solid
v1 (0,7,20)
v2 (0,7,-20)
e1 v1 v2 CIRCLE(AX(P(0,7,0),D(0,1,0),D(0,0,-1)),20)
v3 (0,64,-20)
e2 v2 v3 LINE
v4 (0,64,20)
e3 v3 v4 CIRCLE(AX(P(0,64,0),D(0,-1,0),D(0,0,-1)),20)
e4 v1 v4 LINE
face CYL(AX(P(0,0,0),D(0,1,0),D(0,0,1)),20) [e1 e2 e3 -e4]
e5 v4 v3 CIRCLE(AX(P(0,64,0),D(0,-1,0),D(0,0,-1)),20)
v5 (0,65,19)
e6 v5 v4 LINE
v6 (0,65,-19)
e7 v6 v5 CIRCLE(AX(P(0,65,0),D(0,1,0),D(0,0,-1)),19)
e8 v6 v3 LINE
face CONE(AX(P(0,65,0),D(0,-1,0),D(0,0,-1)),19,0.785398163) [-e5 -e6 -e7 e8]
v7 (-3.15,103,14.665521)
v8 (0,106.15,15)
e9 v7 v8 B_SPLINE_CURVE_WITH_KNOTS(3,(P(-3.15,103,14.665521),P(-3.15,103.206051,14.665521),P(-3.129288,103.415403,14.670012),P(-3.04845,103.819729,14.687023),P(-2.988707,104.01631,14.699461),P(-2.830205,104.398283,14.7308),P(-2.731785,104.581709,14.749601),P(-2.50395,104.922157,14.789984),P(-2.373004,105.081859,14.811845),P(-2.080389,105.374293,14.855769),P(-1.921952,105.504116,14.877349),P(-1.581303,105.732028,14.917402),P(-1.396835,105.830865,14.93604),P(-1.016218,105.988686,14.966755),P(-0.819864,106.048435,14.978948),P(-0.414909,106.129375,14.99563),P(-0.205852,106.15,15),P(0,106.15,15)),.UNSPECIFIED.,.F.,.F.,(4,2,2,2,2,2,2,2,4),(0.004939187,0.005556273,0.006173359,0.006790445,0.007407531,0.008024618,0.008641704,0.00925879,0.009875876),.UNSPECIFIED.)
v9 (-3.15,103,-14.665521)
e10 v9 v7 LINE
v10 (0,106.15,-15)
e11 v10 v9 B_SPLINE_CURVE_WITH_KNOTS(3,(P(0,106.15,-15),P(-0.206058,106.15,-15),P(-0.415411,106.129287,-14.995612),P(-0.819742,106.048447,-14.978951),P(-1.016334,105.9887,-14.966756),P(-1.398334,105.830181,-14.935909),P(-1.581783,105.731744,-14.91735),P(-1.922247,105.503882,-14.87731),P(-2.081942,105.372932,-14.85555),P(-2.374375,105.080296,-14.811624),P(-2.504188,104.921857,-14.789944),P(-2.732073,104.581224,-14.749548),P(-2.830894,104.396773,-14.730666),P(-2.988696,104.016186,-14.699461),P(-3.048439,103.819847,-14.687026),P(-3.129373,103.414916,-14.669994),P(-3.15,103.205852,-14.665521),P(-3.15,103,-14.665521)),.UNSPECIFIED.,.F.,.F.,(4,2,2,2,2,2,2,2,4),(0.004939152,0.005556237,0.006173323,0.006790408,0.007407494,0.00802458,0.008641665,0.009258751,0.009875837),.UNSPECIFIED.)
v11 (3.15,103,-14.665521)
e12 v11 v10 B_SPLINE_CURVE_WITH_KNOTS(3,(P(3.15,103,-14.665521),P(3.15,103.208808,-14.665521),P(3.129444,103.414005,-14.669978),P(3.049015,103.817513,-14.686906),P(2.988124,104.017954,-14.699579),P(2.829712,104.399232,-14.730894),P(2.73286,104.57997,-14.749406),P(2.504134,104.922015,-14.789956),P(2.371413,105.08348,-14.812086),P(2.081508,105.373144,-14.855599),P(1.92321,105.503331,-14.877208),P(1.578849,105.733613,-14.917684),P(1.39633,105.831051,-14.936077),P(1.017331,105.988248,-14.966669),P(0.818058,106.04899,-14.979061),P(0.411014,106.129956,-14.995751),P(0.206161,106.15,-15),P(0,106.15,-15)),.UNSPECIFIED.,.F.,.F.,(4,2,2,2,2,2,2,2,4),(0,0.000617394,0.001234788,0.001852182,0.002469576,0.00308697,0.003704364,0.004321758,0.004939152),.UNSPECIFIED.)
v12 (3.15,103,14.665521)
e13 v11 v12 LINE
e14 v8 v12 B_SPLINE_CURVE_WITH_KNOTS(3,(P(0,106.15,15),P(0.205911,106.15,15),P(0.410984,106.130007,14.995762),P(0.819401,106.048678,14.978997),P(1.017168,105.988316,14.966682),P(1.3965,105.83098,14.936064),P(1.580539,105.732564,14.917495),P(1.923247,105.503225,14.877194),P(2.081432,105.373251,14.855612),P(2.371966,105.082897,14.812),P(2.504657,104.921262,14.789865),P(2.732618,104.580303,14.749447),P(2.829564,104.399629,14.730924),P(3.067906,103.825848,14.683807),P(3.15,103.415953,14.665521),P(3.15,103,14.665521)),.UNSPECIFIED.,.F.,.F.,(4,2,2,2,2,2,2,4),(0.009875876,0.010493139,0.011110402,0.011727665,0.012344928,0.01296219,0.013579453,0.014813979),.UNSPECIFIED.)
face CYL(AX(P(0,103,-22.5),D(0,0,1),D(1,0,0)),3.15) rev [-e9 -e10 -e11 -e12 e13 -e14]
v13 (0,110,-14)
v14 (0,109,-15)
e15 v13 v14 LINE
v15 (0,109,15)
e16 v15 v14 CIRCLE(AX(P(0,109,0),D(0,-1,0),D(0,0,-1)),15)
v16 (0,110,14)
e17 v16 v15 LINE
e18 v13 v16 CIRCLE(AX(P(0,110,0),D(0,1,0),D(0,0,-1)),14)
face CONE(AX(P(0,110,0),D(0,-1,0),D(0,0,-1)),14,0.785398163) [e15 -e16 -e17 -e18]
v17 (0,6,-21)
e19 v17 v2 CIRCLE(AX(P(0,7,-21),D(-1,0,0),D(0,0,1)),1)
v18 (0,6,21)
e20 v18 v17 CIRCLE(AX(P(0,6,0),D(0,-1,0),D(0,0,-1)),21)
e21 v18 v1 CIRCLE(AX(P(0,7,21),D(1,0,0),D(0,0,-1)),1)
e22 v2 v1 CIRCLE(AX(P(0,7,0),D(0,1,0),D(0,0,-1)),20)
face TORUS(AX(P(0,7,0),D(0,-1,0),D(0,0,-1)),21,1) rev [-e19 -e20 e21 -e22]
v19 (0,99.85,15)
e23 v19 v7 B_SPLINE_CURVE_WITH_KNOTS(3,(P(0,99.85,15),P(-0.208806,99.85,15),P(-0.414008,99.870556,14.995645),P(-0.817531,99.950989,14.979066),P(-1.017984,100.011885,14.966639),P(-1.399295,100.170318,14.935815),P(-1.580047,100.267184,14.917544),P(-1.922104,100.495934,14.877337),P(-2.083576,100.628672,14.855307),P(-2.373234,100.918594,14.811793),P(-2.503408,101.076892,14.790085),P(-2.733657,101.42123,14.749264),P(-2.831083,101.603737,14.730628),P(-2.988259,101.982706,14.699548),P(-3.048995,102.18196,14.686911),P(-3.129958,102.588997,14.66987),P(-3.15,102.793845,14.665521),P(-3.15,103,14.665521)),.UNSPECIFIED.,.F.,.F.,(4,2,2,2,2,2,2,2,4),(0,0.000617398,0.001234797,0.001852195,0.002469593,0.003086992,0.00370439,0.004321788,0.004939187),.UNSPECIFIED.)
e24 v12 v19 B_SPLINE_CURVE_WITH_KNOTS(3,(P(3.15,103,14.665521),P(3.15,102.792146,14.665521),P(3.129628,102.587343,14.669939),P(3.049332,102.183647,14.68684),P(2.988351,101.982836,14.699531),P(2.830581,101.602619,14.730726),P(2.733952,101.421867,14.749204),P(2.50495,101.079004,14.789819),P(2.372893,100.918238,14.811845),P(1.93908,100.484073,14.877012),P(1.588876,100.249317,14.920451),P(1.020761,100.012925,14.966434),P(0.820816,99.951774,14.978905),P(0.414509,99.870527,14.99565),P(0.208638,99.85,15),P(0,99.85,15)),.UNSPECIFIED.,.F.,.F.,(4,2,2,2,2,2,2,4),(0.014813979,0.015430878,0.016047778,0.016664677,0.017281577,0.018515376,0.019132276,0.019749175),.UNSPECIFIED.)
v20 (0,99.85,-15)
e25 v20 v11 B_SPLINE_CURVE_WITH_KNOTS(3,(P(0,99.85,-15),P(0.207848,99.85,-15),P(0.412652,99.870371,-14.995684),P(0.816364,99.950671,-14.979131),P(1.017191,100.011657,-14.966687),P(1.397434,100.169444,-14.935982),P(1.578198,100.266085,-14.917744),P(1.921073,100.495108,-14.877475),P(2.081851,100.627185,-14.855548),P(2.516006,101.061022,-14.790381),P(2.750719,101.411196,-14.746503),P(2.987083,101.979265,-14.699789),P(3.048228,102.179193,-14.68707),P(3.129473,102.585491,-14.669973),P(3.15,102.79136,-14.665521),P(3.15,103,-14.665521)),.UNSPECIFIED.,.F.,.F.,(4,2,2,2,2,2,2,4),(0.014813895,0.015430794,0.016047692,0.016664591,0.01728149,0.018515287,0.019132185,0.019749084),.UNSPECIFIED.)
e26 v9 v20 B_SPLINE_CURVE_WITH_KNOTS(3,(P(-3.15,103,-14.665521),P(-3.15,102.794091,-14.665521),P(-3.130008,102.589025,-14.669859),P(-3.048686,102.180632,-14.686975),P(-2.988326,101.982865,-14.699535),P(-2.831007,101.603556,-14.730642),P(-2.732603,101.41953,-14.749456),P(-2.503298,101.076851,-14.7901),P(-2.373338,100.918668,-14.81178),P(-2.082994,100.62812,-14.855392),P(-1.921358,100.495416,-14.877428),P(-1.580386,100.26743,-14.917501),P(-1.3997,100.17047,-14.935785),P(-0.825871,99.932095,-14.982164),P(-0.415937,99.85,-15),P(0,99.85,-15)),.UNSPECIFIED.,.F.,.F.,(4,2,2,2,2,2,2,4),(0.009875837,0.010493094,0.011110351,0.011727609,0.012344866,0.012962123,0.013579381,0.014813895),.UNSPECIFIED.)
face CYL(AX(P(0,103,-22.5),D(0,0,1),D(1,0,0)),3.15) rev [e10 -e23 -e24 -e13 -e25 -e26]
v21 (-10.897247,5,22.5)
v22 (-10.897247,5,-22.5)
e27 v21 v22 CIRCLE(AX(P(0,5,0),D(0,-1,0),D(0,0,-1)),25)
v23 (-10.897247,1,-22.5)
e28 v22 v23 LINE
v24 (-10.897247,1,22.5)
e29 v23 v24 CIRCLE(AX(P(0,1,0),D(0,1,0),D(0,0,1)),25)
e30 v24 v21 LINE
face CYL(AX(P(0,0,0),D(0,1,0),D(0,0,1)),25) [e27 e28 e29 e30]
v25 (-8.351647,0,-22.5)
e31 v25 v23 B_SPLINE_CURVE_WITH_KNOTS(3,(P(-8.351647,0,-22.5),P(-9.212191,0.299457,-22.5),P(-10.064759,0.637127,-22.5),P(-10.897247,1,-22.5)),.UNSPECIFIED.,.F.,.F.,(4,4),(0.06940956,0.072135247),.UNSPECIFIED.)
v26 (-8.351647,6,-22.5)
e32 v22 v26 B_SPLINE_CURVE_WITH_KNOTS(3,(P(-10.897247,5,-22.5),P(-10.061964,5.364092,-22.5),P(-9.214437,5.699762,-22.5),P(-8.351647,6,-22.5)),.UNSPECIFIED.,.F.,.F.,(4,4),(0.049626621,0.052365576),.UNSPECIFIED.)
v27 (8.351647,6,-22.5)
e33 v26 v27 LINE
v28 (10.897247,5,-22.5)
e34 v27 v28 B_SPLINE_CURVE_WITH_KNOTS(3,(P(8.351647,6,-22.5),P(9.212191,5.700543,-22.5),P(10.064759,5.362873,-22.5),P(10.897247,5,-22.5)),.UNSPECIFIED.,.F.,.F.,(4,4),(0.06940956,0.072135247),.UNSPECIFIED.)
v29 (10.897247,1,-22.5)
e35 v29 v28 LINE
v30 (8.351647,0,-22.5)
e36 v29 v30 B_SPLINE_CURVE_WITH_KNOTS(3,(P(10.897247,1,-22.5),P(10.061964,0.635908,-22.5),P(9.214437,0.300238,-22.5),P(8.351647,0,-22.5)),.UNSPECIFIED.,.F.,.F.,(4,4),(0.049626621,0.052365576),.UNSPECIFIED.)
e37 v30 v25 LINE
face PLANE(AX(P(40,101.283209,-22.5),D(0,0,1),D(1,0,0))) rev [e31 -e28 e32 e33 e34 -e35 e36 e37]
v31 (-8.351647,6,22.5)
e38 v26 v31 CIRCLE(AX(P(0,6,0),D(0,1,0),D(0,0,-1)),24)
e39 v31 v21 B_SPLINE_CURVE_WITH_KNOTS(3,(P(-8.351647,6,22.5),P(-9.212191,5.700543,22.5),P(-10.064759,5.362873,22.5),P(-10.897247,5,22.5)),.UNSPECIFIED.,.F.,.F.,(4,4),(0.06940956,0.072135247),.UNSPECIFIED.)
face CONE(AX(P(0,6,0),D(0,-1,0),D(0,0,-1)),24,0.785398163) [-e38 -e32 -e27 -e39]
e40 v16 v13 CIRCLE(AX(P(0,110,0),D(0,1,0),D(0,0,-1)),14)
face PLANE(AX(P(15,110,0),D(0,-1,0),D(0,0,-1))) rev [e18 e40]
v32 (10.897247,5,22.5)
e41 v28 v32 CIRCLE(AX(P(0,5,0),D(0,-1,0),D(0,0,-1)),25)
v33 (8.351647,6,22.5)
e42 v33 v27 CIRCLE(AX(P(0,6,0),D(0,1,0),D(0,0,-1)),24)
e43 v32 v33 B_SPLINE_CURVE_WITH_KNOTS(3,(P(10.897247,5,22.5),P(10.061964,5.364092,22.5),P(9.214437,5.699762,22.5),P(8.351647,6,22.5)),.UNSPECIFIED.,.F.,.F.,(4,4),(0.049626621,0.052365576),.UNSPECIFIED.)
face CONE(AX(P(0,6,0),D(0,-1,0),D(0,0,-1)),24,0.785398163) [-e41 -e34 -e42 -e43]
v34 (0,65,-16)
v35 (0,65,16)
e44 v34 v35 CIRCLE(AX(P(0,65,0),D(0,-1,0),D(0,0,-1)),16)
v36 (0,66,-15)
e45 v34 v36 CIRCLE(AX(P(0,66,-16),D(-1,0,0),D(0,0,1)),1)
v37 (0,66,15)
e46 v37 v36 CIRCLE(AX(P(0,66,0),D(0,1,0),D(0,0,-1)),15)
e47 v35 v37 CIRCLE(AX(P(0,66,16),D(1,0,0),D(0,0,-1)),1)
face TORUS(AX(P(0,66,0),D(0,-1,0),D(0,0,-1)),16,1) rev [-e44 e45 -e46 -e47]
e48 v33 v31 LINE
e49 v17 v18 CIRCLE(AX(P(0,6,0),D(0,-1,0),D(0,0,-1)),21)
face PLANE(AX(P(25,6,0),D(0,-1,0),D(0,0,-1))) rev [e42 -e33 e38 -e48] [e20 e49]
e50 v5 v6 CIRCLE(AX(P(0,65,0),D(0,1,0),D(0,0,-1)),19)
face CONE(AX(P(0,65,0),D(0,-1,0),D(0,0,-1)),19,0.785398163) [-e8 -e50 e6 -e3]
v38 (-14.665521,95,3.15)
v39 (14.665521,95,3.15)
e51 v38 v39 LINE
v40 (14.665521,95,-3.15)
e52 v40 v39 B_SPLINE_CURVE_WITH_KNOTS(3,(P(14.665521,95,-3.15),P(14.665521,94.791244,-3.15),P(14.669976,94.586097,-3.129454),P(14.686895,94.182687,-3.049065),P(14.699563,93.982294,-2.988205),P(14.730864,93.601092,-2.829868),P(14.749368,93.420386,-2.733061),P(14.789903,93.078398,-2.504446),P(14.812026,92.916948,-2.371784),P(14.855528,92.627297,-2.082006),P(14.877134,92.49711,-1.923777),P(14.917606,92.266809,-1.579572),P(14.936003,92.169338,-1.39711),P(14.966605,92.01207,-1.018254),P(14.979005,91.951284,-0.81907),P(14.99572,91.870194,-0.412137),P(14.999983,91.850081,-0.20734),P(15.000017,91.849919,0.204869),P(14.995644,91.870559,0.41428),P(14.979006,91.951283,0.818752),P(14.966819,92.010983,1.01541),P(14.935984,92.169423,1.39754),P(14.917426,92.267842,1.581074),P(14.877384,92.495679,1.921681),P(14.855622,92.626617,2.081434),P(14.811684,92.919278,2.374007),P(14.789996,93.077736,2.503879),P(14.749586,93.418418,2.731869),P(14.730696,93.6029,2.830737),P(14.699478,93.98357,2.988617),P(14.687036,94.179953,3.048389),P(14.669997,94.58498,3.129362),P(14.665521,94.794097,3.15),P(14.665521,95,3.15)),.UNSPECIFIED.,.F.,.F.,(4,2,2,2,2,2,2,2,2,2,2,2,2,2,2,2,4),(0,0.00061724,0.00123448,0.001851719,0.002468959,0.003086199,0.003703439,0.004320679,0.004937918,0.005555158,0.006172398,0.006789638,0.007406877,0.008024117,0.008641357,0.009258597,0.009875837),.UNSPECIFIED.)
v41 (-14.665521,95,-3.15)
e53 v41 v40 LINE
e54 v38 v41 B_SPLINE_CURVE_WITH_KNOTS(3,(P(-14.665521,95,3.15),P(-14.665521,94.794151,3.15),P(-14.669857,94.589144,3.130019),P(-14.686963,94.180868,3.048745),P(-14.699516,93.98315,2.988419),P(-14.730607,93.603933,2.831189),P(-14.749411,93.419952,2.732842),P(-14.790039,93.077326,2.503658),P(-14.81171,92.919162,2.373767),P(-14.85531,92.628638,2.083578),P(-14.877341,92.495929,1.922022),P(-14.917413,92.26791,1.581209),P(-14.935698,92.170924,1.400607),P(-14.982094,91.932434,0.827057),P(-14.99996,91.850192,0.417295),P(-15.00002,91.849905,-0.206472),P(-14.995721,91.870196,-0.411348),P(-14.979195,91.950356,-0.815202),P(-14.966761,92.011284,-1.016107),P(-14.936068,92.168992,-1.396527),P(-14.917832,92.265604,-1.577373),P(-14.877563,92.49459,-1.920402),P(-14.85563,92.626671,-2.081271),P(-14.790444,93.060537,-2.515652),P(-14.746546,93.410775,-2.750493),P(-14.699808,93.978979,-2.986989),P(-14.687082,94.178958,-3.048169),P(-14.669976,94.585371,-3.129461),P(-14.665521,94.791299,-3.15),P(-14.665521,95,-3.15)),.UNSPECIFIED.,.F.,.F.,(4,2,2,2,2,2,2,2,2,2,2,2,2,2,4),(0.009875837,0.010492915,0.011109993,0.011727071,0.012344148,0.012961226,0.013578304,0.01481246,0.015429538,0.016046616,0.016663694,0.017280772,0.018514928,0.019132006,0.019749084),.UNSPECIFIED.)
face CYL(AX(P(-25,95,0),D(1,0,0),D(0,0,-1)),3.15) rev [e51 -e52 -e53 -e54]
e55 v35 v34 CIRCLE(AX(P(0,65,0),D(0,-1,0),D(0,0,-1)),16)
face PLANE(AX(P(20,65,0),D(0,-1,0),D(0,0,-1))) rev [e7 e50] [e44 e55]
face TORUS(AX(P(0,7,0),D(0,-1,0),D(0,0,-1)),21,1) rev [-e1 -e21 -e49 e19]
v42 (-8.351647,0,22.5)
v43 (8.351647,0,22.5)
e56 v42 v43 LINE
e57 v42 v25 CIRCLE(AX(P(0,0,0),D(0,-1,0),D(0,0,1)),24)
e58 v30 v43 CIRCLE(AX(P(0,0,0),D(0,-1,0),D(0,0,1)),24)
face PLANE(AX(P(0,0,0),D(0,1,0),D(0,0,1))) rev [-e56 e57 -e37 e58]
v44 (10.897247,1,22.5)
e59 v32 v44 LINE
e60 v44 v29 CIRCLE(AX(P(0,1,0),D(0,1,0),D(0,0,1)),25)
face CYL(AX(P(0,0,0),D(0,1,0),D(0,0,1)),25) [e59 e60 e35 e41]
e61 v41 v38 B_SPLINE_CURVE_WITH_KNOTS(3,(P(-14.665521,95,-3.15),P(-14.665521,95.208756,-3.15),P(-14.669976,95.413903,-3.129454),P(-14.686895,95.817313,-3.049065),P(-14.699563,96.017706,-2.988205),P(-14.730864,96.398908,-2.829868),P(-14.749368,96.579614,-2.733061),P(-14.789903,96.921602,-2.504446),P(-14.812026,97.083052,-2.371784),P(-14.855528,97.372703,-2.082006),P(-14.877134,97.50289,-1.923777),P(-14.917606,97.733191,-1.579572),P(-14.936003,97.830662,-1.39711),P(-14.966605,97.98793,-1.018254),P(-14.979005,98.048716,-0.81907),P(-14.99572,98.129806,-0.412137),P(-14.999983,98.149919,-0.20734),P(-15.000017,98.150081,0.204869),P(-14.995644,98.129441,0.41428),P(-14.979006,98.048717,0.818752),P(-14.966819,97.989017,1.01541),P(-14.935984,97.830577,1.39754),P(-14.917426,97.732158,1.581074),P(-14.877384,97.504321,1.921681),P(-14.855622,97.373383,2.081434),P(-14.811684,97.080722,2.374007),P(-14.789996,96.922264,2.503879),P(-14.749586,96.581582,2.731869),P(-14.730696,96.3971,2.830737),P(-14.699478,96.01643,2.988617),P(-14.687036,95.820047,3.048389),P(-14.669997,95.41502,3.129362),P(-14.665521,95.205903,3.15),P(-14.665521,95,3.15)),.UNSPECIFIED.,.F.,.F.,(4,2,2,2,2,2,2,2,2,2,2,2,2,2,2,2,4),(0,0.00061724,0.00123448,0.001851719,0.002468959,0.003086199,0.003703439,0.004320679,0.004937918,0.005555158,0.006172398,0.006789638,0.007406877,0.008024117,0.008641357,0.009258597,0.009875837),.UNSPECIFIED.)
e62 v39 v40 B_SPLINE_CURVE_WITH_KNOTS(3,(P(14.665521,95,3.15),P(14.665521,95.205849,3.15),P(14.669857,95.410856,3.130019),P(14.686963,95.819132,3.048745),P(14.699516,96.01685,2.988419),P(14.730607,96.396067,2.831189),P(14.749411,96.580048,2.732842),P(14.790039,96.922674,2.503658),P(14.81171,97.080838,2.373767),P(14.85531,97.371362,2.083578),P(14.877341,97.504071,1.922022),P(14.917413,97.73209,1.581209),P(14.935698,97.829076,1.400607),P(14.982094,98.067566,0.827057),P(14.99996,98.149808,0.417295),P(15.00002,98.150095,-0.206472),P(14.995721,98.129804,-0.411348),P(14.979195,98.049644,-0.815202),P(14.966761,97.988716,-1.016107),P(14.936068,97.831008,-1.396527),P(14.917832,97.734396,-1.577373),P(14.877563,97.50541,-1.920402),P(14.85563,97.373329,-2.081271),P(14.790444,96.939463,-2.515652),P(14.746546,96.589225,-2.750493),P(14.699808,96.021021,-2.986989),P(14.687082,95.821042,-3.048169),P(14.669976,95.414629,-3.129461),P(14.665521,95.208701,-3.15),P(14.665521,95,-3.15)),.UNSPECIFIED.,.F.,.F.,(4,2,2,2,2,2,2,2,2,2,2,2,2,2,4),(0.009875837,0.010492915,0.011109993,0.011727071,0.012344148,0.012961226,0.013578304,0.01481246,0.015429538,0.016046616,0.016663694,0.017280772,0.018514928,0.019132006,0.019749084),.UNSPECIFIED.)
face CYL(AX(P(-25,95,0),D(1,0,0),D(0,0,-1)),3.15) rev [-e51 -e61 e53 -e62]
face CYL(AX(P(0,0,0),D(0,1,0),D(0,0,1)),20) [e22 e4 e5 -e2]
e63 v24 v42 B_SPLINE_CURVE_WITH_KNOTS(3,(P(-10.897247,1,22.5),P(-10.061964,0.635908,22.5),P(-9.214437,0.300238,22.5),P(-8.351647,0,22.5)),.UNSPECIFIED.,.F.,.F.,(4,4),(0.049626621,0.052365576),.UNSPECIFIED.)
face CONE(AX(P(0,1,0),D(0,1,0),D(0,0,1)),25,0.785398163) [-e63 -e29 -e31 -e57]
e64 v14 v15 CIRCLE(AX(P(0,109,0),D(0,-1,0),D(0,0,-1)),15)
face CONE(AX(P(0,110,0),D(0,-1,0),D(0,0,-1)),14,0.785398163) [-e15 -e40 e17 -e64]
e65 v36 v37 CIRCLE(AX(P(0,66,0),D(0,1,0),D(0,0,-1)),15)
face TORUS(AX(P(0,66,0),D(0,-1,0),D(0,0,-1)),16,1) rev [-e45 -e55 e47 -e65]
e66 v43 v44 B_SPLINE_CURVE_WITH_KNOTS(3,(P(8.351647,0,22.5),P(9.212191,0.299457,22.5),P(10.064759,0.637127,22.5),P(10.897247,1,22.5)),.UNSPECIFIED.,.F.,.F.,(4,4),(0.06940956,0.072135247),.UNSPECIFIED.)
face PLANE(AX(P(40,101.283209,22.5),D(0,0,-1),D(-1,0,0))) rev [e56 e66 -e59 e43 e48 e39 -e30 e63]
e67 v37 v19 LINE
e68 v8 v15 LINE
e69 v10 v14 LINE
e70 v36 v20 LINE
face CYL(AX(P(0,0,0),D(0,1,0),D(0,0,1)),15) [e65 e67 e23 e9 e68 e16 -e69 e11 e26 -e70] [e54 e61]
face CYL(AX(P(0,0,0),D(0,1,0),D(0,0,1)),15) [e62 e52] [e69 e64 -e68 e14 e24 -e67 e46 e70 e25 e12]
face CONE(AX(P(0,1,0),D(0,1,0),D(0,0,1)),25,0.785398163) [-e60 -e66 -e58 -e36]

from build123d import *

# Parameters (mm, degrees)
CHAMFER1_SIZE           = 1
FILLET1_R               = 1
SKETCH2_OUTSIDE_W       = 78.154
SKETCH2_OUTSIDE_H       = 78.154
SKETCH2_OUTSIDE_W_2     = 80
SKETCH2_OUTSIDE_H_2     = 45
CUT_EXTRUDE1_DEPTH      = 6
CUT_EXTRUDE2_DEPTH      = 116.027170703
CUT_EXTRUDE2_DEPTH_BACK = 116.027170703
SKETCH3_R               = 3.15
CUT_EXTRUDE3_DEPTH      = 116.027170703
CUT_EXTRUDE3_DEPTH_BACK = 116.027170703
SKETCH4_R               = 3.15


with BuildPart() as part:
    # Sketch1 → Revolve1 (revolve)
    with BuildSketch(Plane.XY, mode=Mode.PRIVATE) as revolve1_sk:
        Polygon((0, 0), (25, 0), (25, 6), (20, 6), (20, 65), (15, 65), (15, 110), (0, 110), align=None)
    revolve(revolve1_sk.sketch.rotate(Axis((0, 0, 0), (0, -1, 0)), 90), axis=Axis((0, 0, 0), (0, -1, 0)))

    # Chamfer1
    chamfer1_edges = [part.edges().sort_by_distance(p)[0] for p in [
        (0, 110, -15),
        (0, 65, -20),
        (0, 6, -25),
        (0, 0, -25),
    ]]
    chamfer(chamfer1_edges, length=CHAMFER1_SIZE)

    # Fillet1
    fillet1_edges = [part.edges().sort_by_distance(p)[0] for p in [
        (0, 65, -15),
        (0, 6, -20),
    ]]
    fillet(fillet1_edges, radius=FILLET1_R)

    # Sketch2 outside → Cut-Extrude1 (cut)
    with BuildSketch(Plane(origin=(0, 0, 0), x_dir=(1, 0, 0), z_dir=(0, 1, 0))):
        Rectangle(SKETCH2_OUTSIDE_W, SKETCH2_OUTSIDE_H)
        Rectangle(SKETCH2_OUTSIDE_W_2, SKETCH2_OUTSIDE_H_2, mode=Mode.SUBTRACT)
    extrude(amount=CUT_EXTRUDE1_DEPTH, mode=Mode.SUBTRACT)

    # Sketch3 → Cut-Extrude2 (cut, two sides: drawn at the far end of the back side and taken through both)
    with BuildSketch(Plane.XY.offset(-CUT_EXTRUDE2_DEPTH_BACK)):
        with Locations(Location((0, 103, 0), (0, 0, 269.99999995))):
            Circle(SKETCH3_R)
    extrude(amount=CUT_EXTRUDE2_DEPTH + CUT_EXTRUDE2_DEPTH_BACK, mode=Mode.SUBTRACT)

    # Sketch4 → Cut-Extrude3 (cut, two sides: drawn at the far end of the back side and taken through both)
    with BuildSketch(Plane(origin=(0, 0, 0), x_dir=(0, 0, -1), z_dir=(1, 0, 0)).offset(-CUT_EXTRUDE3_DEPTH_BACK)):
        with Locations((0, 95)):
            Circle(SKETCH4_R)
    extrude(amount=CUT_EXTRUDE3_DEPTH + CUT_EXTRUDE3_DEPTH_BACK, mode=Mode.SUBTRACT)


solid = part.part
